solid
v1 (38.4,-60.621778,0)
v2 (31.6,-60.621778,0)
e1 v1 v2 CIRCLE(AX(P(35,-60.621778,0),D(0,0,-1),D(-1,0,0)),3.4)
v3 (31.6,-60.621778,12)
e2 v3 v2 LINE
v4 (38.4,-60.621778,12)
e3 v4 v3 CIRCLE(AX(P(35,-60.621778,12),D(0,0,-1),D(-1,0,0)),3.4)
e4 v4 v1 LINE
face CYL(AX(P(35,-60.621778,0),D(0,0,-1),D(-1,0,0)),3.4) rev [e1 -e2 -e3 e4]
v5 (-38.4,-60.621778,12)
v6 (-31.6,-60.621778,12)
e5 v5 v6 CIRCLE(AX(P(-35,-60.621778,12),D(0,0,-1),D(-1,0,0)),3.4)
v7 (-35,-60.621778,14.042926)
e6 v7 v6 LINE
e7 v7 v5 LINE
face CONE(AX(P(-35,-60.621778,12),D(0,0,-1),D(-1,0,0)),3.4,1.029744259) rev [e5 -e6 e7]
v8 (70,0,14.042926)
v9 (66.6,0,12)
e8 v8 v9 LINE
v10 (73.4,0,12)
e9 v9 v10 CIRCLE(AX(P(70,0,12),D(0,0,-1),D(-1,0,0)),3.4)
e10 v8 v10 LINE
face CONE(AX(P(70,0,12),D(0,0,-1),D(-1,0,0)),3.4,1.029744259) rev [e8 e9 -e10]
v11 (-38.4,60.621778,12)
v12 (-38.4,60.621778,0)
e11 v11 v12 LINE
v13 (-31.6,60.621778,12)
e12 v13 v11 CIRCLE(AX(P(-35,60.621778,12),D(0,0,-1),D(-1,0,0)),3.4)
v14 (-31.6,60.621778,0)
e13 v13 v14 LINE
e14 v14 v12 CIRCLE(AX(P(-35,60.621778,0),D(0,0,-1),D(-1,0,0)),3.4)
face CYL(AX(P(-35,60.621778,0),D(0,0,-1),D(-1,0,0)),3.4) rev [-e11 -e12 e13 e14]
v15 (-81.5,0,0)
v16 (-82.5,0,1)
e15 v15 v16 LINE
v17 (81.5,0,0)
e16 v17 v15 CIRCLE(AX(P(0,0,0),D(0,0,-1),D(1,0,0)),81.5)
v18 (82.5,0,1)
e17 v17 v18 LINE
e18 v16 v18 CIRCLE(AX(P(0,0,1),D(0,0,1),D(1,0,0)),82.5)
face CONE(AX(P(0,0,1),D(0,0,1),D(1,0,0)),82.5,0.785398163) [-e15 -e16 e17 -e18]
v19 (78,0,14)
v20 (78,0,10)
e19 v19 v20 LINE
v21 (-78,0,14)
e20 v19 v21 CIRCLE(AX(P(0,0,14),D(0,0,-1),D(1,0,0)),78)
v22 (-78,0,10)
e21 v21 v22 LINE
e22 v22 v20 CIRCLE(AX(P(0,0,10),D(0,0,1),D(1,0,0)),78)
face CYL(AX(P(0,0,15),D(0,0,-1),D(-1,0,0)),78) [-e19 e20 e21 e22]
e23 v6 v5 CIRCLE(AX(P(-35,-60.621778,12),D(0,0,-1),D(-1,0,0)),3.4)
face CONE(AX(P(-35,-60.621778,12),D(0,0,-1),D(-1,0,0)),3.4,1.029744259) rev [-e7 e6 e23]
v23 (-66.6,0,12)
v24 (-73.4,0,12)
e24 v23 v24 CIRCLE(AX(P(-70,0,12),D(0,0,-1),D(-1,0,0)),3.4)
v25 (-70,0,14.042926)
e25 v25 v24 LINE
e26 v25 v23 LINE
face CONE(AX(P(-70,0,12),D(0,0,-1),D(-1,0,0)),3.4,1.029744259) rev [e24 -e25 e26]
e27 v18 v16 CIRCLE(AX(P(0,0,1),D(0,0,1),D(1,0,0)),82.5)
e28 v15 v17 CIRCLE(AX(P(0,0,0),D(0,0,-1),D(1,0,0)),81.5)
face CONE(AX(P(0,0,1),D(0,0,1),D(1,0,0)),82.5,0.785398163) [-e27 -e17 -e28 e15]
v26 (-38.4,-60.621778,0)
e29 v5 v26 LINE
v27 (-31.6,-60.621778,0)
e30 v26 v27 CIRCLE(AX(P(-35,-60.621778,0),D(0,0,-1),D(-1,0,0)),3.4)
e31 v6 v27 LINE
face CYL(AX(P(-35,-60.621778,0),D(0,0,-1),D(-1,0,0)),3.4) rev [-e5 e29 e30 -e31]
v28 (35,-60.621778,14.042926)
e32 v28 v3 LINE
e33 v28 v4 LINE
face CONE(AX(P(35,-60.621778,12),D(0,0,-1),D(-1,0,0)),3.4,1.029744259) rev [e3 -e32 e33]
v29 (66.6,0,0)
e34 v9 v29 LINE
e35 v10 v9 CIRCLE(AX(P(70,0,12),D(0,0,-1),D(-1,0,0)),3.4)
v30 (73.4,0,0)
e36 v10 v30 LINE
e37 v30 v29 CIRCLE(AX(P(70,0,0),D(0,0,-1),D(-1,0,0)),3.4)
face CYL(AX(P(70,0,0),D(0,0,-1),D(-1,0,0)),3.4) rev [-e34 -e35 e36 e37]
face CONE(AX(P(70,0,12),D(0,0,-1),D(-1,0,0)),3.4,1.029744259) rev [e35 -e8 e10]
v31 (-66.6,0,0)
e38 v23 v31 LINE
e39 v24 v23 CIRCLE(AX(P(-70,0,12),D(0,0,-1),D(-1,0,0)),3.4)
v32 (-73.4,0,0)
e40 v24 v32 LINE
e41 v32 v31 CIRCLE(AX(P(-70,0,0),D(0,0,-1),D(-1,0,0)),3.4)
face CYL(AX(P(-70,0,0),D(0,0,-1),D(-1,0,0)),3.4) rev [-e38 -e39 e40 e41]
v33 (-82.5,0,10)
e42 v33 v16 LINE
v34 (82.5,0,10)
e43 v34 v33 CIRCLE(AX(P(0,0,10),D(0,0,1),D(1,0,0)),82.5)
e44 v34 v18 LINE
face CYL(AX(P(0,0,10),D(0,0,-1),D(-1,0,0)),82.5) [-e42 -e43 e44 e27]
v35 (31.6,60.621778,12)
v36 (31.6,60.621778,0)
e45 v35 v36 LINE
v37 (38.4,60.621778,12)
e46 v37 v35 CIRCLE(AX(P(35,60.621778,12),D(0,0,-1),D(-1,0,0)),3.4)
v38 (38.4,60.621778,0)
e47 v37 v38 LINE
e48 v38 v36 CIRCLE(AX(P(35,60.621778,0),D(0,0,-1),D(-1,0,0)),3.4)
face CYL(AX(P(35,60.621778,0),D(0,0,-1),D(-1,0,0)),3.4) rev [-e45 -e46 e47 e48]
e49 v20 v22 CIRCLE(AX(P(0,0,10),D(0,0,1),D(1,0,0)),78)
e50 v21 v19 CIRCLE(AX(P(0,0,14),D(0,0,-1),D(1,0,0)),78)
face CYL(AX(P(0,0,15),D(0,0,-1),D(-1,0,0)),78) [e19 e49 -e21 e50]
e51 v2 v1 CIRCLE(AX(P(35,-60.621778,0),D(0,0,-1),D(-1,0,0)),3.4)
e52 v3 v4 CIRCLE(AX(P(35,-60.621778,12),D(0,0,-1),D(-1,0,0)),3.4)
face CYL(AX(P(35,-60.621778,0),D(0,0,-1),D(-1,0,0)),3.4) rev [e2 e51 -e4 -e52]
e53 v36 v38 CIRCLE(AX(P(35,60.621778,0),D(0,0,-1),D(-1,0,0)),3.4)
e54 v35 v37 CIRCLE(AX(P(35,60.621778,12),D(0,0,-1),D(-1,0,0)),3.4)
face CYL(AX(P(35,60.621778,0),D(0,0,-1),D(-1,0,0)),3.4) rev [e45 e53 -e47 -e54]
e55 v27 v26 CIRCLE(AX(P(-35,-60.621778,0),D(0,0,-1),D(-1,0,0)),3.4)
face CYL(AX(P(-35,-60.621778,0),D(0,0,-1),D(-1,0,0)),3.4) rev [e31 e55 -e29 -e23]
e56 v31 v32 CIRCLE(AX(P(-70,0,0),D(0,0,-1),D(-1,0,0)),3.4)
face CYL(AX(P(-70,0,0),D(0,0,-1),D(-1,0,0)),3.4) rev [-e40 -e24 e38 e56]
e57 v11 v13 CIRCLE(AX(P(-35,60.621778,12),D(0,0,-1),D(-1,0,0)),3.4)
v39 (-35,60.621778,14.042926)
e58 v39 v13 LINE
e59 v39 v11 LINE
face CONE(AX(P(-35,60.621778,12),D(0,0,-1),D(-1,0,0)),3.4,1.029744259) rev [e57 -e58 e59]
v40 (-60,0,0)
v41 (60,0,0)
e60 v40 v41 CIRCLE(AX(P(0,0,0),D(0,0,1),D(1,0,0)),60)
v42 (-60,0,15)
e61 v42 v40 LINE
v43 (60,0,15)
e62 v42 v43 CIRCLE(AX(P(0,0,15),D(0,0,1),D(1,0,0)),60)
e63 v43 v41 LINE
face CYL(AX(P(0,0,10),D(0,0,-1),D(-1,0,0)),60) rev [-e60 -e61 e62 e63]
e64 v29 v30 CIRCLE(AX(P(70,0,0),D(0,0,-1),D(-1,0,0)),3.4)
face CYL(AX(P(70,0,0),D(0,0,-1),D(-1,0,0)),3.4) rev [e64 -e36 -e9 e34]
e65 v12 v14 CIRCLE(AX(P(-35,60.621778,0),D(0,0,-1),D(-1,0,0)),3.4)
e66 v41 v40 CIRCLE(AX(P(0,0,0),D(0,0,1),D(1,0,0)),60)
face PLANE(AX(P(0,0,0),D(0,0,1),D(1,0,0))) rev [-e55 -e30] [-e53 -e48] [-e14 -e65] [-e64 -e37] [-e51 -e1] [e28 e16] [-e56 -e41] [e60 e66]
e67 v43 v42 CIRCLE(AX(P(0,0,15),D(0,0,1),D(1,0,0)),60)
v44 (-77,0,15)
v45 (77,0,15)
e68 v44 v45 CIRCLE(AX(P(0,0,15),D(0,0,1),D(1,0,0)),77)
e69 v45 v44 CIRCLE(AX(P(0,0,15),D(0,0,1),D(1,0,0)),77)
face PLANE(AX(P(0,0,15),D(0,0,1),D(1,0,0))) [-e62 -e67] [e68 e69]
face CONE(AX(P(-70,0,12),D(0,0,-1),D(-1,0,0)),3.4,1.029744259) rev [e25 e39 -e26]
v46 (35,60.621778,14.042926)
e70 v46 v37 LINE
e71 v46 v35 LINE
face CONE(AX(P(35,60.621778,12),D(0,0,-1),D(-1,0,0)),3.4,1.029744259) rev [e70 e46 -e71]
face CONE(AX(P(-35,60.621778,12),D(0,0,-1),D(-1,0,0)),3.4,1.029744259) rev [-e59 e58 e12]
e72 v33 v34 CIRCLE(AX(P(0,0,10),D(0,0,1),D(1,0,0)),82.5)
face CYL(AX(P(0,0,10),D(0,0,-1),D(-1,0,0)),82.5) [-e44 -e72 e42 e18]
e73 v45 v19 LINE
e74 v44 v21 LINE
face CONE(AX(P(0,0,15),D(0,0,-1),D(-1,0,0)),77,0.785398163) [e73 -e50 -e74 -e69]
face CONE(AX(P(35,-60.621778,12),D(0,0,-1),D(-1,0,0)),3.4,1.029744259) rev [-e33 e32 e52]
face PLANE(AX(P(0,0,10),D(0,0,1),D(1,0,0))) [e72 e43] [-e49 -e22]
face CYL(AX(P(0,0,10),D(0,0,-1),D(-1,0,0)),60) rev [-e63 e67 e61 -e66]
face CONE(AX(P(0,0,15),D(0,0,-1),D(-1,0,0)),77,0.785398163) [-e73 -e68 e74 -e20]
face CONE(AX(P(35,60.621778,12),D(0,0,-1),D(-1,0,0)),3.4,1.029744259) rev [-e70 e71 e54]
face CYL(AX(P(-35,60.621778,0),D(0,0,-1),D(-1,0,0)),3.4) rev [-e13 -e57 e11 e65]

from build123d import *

# Parameters (mm, degrees)
SKETCH1_R             = 82.5
SKETCH1_R_2           = 60
BOSS_EXTRUDE1_DEPTH   = 10
SKETCH2_R             = 78
SKETCH2_R_2           = 60
BOSS_EXTRUDE2_DEPTH   = 5
CHAMFER1_SIZE         = 1
M8_TAPPED_HOLE1_D     = 6.8
M8_TAPPED_HOLE1_DEPTH = 12
M8_TAPPED_HOLE1_TIP   = 2.042926105


with BuildPart() as part:
    # Sketch1 → Boss-Extrude1 (new body)
    with BuildSketch(Plane.XY):
        Circle(SKETCH1_R)
        Circle(SKETCH1_R_2, mode=Mode.SUBTRACT)
    extrude(amount=BOSS_EXTRUDE1_DEPTH)

    # Sketch2 → Boss-Extrude2 (add)
    with BuildSketch(Plane.XY.offset(10)):
        Circle(SKETCH2_R)
        Circle(SKETCH2_R_2, mode=Mode.SUBTRACT)
    extrude(amount=BOSS_EXTRUDE2_DEPTH)

    # Chamfer1
    chamfer1_edges = [part.edges().sort_by_distance(p)[0] for p in [
        (-78, 0, 15),
        (-82.5, 0, 0),
    ]]
    chamfer(chamfer1_edges, length=CHAMFER1_SIZE)

    # M8 Tapped Hole1
    with Locations(Plane(origin=(35, 60.621778265, 0), x_dir=(-1, 0, 0), z_dir=(0, 0, -1))):
        with Locations((0, 0), (70, 0), (105, -60.621778265), (70, -121.24355653), (0, -121.24355653), (-35, -60.621778265)):
            Hole(M8_TAPPED_HOLE1_D / 2, depth=M8_TAPPED_HOLE1_DEPTH)
            with Locations((0, 0, -(M8_TAPPED_HOLE1_DEPTH + M8_TAPPED_HOLE1_TIP / 2))):  # 118° drill point
                Cone(0, M8_TAPPED_HOLE1_D / 2, M8_TAPPED_HOLE1_TIP, mode=Mode.SUBTRACT)


solid = part.part
